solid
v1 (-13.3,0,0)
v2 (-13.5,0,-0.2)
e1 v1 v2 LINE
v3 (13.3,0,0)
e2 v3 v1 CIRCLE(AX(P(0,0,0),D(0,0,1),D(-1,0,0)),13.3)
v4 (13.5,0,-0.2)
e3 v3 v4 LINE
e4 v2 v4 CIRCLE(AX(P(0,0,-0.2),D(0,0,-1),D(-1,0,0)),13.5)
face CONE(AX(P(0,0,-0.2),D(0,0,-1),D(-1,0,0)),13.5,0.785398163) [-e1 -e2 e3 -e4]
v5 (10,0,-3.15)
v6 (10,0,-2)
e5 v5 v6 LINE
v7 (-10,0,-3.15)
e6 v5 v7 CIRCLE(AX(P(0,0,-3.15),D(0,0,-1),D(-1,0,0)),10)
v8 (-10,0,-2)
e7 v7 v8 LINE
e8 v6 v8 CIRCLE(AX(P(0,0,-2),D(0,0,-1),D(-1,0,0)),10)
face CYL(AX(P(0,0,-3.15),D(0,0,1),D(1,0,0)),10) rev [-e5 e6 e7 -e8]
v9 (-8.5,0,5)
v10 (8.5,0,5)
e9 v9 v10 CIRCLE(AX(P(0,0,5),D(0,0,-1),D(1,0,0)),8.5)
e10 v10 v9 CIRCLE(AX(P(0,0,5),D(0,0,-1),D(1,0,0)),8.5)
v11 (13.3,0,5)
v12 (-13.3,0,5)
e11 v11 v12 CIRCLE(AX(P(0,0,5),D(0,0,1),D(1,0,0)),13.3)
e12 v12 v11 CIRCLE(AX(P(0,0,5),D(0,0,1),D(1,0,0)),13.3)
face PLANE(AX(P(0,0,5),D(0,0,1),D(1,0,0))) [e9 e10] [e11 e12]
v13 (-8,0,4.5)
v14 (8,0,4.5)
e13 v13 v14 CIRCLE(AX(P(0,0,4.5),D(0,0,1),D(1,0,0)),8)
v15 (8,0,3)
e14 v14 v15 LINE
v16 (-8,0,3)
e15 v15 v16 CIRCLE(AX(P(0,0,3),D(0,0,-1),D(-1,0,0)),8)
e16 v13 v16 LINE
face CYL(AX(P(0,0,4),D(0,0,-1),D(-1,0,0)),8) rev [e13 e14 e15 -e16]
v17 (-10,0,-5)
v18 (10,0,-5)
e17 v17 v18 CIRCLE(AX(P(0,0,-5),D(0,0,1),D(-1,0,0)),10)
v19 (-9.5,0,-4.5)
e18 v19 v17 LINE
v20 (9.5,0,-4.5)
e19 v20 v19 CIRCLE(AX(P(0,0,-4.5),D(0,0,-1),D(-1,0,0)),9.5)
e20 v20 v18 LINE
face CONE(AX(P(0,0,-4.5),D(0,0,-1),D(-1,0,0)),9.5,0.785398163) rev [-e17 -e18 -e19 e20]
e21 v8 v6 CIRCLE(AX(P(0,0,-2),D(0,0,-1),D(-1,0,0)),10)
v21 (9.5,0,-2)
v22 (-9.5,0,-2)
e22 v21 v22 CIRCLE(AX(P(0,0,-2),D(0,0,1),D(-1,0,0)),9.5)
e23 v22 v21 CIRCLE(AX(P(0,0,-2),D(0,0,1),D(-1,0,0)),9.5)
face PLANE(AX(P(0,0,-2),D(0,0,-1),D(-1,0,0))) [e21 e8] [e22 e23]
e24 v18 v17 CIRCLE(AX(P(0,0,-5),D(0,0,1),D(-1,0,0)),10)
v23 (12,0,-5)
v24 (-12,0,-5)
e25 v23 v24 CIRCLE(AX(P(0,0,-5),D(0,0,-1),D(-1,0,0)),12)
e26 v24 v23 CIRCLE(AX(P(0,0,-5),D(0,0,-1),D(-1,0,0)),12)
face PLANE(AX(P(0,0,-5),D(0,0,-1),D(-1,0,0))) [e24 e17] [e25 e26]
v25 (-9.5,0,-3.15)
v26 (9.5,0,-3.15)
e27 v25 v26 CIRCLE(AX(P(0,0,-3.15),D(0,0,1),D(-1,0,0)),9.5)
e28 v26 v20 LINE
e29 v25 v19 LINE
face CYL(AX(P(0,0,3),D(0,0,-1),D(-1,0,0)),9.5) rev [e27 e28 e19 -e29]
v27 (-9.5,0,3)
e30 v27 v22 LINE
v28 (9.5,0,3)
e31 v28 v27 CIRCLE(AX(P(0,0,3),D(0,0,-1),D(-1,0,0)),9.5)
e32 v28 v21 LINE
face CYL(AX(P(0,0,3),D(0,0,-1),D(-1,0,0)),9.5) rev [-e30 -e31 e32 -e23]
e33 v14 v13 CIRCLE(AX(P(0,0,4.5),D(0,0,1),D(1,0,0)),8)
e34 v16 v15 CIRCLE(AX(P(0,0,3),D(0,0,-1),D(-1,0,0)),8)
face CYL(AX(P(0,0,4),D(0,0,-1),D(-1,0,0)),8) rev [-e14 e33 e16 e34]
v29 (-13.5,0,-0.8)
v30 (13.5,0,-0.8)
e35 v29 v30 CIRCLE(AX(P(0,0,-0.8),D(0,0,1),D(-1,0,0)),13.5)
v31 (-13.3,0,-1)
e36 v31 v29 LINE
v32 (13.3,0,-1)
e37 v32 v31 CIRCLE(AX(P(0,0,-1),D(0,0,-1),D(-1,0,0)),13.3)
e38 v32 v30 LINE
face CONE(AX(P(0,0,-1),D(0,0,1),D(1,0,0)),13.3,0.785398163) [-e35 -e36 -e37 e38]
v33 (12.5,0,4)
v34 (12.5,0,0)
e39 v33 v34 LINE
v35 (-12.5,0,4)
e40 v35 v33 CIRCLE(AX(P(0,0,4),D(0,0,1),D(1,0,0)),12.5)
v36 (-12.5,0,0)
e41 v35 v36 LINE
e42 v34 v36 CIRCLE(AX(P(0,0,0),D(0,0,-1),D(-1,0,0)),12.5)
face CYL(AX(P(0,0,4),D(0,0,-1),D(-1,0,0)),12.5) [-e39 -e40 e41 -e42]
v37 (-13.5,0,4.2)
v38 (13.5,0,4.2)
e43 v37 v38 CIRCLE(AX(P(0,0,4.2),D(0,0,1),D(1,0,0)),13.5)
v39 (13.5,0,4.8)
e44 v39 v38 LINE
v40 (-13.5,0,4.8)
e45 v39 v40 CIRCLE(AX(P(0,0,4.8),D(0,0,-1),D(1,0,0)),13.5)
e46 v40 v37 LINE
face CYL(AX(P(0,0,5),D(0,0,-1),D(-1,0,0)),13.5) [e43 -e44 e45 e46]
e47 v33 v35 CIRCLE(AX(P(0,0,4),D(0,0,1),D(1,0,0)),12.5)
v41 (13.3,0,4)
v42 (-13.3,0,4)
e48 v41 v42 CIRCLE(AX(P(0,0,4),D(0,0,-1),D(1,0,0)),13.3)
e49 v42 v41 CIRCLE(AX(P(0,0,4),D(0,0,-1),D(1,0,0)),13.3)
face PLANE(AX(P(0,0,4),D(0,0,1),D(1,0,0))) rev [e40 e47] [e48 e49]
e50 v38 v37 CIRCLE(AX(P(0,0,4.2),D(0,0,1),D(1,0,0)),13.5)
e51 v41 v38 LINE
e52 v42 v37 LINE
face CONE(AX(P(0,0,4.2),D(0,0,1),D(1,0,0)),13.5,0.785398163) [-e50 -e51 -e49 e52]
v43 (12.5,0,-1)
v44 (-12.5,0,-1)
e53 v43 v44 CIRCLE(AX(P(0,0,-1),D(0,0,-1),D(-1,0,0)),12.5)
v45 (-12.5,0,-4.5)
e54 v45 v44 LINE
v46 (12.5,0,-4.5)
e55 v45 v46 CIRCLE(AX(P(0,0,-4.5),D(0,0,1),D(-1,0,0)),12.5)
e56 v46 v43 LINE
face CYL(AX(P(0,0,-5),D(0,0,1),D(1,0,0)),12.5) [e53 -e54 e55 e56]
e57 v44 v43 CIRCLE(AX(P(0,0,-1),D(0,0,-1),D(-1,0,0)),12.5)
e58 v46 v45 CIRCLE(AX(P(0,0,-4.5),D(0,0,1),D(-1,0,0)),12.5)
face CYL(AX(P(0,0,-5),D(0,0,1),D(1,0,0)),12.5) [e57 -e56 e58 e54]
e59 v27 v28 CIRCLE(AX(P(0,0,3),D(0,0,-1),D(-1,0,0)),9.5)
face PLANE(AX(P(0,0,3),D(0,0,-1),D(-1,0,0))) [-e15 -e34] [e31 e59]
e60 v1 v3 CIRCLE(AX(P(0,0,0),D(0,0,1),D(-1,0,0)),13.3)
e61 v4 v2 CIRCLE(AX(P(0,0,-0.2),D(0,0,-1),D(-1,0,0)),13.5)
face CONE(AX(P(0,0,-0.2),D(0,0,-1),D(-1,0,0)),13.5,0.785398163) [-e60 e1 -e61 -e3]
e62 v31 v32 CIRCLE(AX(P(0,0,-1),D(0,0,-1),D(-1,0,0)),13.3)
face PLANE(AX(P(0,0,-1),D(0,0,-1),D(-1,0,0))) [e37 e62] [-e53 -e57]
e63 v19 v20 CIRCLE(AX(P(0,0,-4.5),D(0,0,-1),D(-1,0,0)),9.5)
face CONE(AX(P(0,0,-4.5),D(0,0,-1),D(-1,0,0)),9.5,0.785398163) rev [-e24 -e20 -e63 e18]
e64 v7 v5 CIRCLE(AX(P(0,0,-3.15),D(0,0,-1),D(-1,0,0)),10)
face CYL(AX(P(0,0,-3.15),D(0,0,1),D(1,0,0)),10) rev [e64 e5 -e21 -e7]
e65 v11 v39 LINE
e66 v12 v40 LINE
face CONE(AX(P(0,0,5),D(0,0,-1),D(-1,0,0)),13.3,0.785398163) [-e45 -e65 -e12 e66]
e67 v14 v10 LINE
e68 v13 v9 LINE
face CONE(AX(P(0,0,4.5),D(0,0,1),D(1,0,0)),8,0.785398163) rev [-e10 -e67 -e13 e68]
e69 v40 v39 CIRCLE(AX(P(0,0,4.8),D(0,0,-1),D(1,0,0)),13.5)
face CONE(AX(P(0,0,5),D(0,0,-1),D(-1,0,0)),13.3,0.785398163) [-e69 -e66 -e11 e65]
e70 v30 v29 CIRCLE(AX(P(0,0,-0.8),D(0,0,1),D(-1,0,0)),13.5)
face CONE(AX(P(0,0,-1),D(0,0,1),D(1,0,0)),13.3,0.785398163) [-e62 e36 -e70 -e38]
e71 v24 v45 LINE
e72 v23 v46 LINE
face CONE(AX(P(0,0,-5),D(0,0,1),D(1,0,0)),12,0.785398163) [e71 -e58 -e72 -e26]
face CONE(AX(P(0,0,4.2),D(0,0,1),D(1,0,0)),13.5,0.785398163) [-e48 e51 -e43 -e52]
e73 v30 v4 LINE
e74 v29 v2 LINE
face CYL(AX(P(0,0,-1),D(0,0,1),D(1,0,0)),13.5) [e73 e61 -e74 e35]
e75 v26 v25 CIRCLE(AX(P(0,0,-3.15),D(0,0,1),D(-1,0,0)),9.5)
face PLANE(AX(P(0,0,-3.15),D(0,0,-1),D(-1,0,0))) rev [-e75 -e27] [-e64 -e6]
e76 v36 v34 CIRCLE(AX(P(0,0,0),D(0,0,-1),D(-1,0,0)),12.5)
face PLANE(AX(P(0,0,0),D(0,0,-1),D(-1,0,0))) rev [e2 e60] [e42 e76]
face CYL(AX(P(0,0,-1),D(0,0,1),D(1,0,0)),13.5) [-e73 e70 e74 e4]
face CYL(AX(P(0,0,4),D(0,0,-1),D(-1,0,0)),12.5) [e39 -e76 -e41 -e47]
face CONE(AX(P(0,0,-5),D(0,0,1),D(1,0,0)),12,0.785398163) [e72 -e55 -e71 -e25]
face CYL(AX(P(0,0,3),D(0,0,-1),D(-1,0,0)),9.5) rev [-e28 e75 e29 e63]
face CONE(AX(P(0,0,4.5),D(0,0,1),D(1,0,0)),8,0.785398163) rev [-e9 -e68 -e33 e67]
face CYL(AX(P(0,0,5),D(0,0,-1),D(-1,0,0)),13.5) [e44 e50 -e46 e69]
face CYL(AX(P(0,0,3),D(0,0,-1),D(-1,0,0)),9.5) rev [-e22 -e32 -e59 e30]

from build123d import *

# Parameters (mm, degrees)
SKETCH_1_R          = 12.5
SKETCH_1_R_2        = 8
EXTRUDE_1_DEPTH     = 4
SKETCH_2_R          = 13.5
SKETCH_2_R_2        = 8
EXTRUDE_2_DEPTH     = 1
EXTRUDE_START       = 1
SKETCH_3_R          = 13.5
SKETCH_3_R_2        = 8
EXTRUDE_3_DEPTH     = 1
SKETCH_4_R          = 9.5
CUT_EXTRUDE_1_DEPTH = 4
EXTRUDE_START_2     = 4
SKETCH_7_R          = 12.5
SKETCH_7_R_2        = 9.5
EXTRUDE_4_DEPTH     = 4
CUT_EXTRUDE_START   = -3
SKETCH_8_R          = 10
SKETCH_8_R_2        = 6
CUT_EXTRUDE_2_DEPTH = 1.15
CHAMFER_1_SIZE      = 0.5
CHAMFER_2_SIZE      = 0.2


with BuildPart() as part:
    # 草图1 → 凸台-拉伸1 (new body)
    with BuildSketch(Plane.XY):
        Circle(SKETCH_1_R)
        Circle(SKETCH_1_R_2, mode=Mode.SUBTRACT)
    extrude(amount=EXTRUDE_1_DEPTH)

    # 草图2 → 凸台-拉伸2 (add)
    with BuildSketch(Plane.XY.offset(4)):
        Circle(SKETCH_2_R)
        Circle(SKETCH_2_R_2, mode=Mode.SUBTRACT)
    extrude(amount=EXTRUDE_2_DEPTH)

    # 草图3 → 凸台-拉伸3 (add)
    with BuildSketch(Plane(origin=(0, 0, 0), x_dir=(-1, 0, 0), z_dir=(0, 0, -1)).offset(EXTRUDE_START)):
        with Locations(Location((0, 0, 0), (0, 0, 180))):
            Circle(SKETCH_3_R)
        Circle(SKETCH_3_R_2, mode=Mode.SUBTRACT)
    extrude(amount=-EXTRUDE_3_DEPTH)

    # 草图4 → 切除-拉伸1 (cut)
    with BuildSketch(Plane(origin=(0, 0, -1), x_dir=(-1, 0, 0), z_dir=(0, 0, -1))):
        Circle(SKETCH_4_R)
    extrude(amount=-CUT_EXTRUDE_1_DEPTH, mode=Mode.SUBTRACT)

    # 草图7 → 凸台-拉伸4 (add)
    with BuildSketch(Plane(origin=(0, 0, -1), x_dir=(-1, 0, 0), z_dir=(0, 0, -1)).offset(EXTRUDE_START_2)):
        Circle(SKETCH_7_R)
        Circle(SKETCH_7_R_2, mode=Mode.SUBTRACT)
    extrude(amount=-EXTRUDE_4_DEPTH)

    # 草图8 → 切除-拉伸2 (cut)
    with BuildSketch(Plane(origin=(0, 0, -5), x_dir=(-1, 0, 0), z_dir=(0, 0, -1)).offset(CUT_EXTRUDE_START)):
        Circle(SKETCH_8_R)
        Circle(SKETCH_8_R_2, mode=Mode.SUBTRACT)
    extrude(amount=CUT_EXTRUDE_2_DEPTH, mode=Mode.SUBTRACT)

    # 倒角1
    chamfer_1_edges = [part.edges().sort_by_distance(p)[0] for p in [
        (-8, 0, 5),
        (12.5, 0, -5),
        (9.5, 0, -5),
    ]]
    chamfer(chamfer_1_edges, length=CHAMFER_1_SIZE)

    # 倒角2
    chamfer_2_edges = [part.edges().sort_by_distance(p)[0] for p in [
        (-13.5, 0, 4),
        (-13.5, 0, -1),
        (-13.5, 0, 0),
        (-13.5, 0, 5),
    ]]
    chamfer(chamfer_2_edges, length=CHAMFER_2_SIZE)


solid = part.part
